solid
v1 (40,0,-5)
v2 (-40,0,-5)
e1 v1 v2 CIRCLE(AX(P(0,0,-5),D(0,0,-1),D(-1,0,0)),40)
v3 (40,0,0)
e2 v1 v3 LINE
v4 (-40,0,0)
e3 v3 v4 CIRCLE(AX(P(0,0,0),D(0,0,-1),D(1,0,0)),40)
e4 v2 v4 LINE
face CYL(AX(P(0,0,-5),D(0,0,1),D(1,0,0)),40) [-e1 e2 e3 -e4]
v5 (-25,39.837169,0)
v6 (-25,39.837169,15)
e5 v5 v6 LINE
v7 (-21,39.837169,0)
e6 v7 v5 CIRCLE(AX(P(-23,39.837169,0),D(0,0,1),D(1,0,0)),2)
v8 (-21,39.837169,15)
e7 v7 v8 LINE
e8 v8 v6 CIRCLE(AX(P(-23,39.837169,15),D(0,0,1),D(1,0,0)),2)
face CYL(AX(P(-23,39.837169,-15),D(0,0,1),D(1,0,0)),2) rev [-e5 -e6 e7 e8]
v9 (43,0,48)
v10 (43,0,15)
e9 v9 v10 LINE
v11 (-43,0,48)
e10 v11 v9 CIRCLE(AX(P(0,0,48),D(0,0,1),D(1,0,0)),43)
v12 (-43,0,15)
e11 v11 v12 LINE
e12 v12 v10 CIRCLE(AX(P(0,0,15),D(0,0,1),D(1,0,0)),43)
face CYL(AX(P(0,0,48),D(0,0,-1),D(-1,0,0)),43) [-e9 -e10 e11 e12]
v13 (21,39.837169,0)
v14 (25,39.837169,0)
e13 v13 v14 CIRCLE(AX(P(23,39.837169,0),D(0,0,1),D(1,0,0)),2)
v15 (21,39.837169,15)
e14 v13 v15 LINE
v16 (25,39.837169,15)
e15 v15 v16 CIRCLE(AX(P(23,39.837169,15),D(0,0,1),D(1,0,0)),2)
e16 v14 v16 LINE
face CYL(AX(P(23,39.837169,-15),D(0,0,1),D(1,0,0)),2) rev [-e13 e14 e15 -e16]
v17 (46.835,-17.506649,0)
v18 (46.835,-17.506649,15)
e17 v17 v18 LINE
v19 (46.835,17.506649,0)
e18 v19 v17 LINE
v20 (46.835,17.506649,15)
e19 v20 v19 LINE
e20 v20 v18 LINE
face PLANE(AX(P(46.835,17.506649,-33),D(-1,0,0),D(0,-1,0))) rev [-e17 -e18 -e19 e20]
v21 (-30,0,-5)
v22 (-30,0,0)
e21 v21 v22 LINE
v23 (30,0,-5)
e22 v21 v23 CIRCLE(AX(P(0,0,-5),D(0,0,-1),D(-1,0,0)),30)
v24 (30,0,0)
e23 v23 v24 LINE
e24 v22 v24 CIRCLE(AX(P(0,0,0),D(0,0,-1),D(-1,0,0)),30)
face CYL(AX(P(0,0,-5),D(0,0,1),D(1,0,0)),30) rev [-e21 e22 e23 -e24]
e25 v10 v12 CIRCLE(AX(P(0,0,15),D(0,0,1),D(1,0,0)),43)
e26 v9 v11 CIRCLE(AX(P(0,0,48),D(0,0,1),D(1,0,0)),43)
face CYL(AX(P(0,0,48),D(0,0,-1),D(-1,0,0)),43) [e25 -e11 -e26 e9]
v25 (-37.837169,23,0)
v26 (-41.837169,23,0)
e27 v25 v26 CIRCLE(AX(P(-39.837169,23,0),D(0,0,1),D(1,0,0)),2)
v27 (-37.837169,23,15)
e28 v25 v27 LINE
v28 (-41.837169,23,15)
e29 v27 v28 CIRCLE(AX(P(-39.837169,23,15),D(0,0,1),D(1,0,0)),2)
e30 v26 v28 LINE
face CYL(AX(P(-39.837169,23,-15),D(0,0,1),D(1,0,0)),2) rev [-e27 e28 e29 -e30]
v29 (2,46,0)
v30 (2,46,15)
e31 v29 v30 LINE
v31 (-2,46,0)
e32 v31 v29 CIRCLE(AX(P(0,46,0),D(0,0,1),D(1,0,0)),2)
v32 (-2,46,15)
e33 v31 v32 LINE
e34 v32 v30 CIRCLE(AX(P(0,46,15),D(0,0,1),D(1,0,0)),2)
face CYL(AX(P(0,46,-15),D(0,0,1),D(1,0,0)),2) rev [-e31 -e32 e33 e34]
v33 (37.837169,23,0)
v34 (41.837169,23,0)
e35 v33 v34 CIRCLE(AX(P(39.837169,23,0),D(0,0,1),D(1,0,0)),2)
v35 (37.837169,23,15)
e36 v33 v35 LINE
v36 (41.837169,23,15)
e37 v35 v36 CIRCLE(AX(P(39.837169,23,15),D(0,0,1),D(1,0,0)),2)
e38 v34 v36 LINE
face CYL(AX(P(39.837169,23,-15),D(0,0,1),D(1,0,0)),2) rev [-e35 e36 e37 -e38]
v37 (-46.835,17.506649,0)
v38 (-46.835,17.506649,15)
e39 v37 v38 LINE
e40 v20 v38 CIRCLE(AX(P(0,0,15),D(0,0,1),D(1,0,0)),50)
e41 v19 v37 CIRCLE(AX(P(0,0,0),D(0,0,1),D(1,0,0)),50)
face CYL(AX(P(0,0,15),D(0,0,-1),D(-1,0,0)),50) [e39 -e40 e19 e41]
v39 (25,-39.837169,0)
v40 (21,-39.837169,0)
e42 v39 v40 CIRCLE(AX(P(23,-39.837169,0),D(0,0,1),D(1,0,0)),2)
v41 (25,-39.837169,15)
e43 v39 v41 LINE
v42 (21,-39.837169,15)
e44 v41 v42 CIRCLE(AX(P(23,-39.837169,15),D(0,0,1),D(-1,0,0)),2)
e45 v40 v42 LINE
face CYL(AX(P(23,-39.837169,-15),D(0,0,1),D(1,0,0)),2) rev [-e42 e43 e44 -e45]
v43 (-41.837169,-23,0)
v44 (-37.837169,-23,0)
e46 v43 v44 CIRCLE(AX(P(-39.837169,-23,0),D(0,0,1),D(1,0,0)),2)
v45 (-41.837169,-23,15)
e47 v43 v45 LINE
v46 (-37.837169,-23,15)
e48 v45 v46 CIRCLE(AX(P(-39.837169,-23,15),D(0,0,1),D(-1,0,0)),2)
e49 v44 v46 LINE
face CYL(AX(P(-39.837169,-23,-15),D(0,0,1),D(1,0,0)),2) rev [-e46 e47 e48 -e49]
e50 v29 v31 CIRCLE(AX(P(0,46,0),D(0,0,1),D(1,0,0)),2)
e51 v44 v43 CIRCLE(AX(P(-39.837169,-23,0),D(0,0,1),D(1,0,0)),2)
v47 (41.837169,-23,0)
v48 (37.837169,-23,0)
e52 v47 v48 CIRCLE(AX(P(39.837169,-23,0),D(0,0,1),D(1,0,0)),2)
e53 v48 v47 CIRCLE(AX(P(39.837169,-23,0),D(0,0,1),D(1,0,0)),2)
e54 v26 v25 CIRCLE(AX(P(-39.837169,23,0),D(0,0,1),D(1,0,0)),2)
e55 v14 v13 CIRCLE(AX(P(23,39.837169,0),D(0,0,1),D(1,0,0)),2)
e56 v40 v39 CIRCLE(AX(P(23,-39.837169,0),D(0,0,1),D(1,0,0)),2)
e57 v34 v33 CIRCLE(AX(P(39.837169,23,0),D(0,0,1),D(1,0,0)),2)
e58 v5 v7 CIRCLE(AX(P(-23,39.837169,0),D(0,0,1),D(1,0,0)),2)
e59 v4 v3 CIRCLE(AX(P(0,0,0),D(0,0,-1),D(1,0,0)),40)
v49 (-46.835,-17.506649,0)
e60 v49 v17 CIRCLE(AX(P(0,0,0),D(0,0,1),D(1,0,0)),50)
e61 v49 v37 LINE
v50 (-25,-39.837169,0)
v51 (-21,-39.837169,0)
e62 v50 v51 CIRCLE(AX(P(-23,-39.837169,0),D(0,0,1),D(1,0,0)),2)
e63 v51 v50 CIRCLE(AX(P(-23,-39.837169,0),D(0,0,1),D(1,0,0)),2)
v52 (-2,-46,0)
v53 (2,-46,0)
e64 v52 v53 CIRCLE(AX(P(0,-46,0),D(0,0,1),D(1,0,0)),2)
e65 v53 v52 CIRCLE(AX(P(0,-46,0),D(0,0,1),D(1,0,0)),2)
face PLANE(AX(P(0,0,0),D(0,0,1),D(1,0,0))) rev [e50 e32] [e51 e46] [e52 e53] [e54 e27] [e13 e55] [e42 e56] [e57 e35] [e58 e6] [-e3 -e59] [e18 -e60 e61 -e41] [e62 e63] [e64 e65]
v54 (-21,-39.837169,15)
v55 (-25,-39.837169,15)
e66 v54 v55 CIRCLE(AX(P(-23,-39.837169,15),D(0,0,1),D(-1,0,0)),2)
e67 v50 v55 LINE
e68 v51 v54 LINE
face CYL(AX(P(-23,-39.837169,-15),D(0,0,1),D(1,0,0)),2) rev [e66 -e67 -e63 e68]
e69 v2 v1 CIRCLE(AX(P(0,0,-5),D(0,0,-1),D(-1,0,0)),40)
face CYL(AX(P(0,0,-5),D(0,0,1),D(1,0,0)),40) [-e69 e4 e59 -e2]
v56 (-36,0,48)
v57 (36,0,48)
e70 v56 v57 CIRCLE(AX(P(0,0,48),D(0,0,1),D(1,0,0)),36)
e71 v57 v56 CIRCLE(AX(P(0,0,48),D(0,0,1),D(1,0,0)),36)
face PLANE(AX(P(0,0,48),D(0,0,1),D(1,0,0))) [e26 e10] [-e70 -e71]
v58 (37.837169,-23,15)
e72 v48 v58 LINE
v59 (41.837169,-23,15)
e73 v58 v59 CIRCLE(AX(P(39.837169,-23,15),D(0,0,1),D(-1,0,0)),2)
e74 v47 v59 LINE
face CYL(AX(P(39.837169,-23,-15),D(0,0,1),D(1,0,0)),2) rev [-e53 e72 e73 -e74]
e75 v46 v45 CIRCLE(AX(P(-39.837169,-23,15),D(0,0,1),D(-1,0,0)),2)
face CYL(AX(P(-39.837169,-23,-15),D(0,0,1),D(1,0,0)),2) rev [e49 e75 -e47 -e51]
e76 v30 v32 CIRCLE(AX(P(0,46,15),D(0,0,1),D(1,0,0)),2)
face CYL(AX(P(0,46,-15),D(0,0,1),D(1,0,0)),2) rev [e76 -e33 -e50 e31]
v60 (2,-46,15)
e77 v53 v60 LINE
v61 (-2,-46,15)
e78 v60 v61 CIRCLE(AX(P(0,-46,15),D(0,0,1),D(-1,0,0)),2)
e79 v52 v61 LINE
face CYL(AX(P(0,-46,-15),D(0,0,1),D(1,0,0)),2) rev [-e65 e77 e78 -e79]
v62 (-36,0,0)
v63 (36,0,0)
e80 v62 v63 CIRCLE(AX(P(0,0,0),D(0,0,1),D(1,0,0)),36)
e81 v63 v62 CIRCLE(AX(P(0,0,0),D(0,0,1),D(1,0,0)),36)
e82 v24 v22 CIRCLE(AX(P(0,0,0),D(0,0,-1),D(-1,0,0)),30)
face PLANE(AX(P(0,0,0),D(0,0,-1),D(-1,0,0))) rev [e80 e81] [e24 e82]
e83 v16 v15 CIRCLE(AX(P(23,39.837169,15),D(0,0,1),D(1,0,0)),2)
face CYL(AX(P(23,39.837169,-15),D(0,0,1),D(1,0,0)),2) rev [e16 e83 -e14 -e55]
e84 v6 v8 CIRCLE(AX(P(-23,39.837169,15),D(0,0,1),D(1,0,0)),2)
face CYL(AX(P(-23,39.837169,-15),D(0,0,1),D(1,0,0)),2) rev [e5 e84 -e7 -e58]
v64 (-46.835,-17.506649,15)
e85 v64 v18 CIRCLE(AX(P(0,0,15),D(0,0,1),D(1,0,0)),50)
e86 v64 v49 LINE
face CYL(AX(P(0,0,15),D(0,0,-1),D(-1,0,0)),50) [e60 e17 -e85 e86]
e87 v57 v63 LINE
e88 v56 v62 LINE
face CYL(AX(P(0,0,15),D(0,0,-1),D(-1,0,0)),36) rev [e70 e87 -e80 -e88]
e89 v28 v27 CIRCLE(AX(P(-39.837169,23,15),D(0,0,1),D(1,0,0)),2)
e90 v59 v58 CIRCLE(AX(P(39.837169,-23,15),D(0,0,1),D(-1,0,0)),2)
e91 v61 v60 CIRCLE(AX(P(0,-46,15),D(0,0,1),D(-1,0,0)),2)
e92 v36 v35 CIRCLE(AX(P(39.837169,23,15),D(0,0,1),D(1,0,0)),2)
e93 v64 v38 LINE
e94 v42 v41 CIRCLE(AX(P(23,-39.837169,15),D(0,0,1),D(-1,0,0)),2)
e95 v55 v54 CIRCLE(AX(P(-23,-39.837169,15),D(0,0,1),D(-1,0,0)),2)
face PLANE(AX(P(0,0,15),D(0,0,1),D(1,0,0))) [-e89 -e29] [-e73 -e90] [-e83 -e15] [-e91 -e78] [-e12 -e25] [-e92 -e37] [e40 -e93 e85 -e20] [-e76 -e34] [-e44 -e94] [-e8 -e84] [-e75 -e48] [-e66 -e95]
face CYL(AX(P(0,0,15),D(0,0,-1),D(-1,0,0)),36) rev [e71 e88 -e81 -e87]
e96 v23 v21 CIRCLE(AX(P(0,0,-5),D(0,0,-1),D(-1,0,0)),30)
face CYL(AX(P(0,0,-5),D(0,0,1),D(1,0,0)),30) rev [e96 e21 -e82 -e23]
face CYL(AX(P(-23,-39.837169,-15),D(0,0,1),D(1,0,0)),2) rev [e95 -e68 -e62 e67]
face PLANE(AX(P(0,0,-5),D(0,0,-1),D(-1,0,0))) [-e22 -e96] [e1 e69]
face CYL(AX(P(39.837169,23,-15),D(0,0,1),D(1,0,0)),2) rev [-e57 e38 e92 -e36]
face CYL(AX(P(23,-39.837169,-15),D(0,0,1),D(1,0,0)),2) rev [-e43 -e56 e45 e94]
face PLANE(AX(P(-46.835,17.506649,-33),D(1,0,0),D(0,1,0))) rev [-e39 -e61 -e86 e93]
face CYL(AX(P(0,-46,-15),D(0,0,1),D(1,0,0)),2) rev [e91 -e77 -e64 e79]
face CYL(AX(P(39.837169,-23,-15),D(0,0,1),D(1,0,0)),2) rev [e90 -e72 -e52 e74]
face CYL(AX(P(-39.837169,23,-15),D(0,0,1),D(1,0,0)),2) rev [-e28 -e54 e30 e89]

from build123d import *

# Parameters (mm, degrees)
SKETCH1_R           = 50
SKETCH1_R_2         = 36
BOSS_EXTRUDE1_DEPTH = 15
CUT_EXTRUDE1_START  = -48
CUT_EXTRUDE1_DEPTH  = 48
SKETCH4_R           = 40
SKETCH4_R_2         = 30
BOSS_EXTRUDE2_DEPTH = 5
SKETCH5_R           = 43
SKETCH5_R_2         = 36
BOSS_EXTRUDE3_DEPTH = 33
SKETCH6_R           = 2
CUT_EXTRUDE2_DEPTH  = 30


with BuildPart() as part:
    # Sketch1 → Boss-Extrude1 (new body)
    with BuildSketch(Plane.XY):
        Circle(SKETCH1_R)
        Circle(SKETCH1_R_2, mode=Mode.SUBTRACT)
    extrude(amount=BOSS_EXTRUDE1_DEPTH)

    # Sketch2 → Cut-Extrude1 (cut)
    with BuildSketch(Plane.XY.offset(15).offset(CUT_EXTRUDE1_START)):
        with BuildLine():
            Line((-46.835, 17.506649451), (-46.835, -17.506649451))
            ThreePointArc((-46.835, -17.506649451), (-50, 0), (-46.835, 17.506649451))
        make_face()
        with BuildLine():
            Line((46.835, 17.506649451), (46.835, -17.506649451))
            ThreePointArc((46.835, -17.506649451), (50, 0), (46.835, 17.506649451))
        make_face()
    extrude(amount=CUT_EXTRUDE1_DEPTH, mode=Mode.SUBTRACT)

    # Sketch4 → Boss-Extrude2 (add)
    with BuildSketch(Plane(origin=(0, 0, 0), x_dir=(-1, 0, 0), z_dir=(0, 0, -1))):
        with Locations(Location((0, 0, 0), (0, 0, 180))):
            Circle(SKETCH4_R)
        Circle(SKETCH4_R_2, mode=Mode.SUBTRACT)
    extrude(amount=BOSS_EXTRUDE2_DEPTH)

    # Sketch5 → Boss-Extrude3 (add)
    with BuildSketch(Plane.XY.offset(15)):
        Circle(SKETCH5_R)
        Circle(SKETCH5_R_2, mode=Mode.SUBTRACT)
    extrude(amount=BOSS_EXTRUDE3_DEPTH)

    # Sketch6 → Cut-Extrude2 (cut)
    with BuildSketch(Plane.XY.offset(15)):
        with Locations((0, 46)):
            Circle(SKETCH6_R)
        with Locations((39.837168574, -23)):
            Circle(SKETCH6_R)
        with Locations((23, 39.837168574)):
            Circle(SKETCH6_R)
        with Locations((39.837168574, 23)):
            Circle(SKETCH6_R)
        with Locations((-23, 39.837168574)):
            Circle(SKETCH6_R)
        with Locations((-39.837168574, 23)):
            Circle(SKETCH6_R)
        with Locations((23, -39.837168574)):
            Circle(SKETCH6_R)
        with Locations((0, -46)):
            Circle(SKETCH6_R)
        with Locations((-23, -39.837168574)):
            Circle(SKETCH6_R)
        with Locations((-39.837168574, -23)):
            Circle(SKETCH6_R)
    extrude(amount=-CUT_EXTRUDE2_DEPTH, mode=Mode.SUBTRACT)


solid = part.part
